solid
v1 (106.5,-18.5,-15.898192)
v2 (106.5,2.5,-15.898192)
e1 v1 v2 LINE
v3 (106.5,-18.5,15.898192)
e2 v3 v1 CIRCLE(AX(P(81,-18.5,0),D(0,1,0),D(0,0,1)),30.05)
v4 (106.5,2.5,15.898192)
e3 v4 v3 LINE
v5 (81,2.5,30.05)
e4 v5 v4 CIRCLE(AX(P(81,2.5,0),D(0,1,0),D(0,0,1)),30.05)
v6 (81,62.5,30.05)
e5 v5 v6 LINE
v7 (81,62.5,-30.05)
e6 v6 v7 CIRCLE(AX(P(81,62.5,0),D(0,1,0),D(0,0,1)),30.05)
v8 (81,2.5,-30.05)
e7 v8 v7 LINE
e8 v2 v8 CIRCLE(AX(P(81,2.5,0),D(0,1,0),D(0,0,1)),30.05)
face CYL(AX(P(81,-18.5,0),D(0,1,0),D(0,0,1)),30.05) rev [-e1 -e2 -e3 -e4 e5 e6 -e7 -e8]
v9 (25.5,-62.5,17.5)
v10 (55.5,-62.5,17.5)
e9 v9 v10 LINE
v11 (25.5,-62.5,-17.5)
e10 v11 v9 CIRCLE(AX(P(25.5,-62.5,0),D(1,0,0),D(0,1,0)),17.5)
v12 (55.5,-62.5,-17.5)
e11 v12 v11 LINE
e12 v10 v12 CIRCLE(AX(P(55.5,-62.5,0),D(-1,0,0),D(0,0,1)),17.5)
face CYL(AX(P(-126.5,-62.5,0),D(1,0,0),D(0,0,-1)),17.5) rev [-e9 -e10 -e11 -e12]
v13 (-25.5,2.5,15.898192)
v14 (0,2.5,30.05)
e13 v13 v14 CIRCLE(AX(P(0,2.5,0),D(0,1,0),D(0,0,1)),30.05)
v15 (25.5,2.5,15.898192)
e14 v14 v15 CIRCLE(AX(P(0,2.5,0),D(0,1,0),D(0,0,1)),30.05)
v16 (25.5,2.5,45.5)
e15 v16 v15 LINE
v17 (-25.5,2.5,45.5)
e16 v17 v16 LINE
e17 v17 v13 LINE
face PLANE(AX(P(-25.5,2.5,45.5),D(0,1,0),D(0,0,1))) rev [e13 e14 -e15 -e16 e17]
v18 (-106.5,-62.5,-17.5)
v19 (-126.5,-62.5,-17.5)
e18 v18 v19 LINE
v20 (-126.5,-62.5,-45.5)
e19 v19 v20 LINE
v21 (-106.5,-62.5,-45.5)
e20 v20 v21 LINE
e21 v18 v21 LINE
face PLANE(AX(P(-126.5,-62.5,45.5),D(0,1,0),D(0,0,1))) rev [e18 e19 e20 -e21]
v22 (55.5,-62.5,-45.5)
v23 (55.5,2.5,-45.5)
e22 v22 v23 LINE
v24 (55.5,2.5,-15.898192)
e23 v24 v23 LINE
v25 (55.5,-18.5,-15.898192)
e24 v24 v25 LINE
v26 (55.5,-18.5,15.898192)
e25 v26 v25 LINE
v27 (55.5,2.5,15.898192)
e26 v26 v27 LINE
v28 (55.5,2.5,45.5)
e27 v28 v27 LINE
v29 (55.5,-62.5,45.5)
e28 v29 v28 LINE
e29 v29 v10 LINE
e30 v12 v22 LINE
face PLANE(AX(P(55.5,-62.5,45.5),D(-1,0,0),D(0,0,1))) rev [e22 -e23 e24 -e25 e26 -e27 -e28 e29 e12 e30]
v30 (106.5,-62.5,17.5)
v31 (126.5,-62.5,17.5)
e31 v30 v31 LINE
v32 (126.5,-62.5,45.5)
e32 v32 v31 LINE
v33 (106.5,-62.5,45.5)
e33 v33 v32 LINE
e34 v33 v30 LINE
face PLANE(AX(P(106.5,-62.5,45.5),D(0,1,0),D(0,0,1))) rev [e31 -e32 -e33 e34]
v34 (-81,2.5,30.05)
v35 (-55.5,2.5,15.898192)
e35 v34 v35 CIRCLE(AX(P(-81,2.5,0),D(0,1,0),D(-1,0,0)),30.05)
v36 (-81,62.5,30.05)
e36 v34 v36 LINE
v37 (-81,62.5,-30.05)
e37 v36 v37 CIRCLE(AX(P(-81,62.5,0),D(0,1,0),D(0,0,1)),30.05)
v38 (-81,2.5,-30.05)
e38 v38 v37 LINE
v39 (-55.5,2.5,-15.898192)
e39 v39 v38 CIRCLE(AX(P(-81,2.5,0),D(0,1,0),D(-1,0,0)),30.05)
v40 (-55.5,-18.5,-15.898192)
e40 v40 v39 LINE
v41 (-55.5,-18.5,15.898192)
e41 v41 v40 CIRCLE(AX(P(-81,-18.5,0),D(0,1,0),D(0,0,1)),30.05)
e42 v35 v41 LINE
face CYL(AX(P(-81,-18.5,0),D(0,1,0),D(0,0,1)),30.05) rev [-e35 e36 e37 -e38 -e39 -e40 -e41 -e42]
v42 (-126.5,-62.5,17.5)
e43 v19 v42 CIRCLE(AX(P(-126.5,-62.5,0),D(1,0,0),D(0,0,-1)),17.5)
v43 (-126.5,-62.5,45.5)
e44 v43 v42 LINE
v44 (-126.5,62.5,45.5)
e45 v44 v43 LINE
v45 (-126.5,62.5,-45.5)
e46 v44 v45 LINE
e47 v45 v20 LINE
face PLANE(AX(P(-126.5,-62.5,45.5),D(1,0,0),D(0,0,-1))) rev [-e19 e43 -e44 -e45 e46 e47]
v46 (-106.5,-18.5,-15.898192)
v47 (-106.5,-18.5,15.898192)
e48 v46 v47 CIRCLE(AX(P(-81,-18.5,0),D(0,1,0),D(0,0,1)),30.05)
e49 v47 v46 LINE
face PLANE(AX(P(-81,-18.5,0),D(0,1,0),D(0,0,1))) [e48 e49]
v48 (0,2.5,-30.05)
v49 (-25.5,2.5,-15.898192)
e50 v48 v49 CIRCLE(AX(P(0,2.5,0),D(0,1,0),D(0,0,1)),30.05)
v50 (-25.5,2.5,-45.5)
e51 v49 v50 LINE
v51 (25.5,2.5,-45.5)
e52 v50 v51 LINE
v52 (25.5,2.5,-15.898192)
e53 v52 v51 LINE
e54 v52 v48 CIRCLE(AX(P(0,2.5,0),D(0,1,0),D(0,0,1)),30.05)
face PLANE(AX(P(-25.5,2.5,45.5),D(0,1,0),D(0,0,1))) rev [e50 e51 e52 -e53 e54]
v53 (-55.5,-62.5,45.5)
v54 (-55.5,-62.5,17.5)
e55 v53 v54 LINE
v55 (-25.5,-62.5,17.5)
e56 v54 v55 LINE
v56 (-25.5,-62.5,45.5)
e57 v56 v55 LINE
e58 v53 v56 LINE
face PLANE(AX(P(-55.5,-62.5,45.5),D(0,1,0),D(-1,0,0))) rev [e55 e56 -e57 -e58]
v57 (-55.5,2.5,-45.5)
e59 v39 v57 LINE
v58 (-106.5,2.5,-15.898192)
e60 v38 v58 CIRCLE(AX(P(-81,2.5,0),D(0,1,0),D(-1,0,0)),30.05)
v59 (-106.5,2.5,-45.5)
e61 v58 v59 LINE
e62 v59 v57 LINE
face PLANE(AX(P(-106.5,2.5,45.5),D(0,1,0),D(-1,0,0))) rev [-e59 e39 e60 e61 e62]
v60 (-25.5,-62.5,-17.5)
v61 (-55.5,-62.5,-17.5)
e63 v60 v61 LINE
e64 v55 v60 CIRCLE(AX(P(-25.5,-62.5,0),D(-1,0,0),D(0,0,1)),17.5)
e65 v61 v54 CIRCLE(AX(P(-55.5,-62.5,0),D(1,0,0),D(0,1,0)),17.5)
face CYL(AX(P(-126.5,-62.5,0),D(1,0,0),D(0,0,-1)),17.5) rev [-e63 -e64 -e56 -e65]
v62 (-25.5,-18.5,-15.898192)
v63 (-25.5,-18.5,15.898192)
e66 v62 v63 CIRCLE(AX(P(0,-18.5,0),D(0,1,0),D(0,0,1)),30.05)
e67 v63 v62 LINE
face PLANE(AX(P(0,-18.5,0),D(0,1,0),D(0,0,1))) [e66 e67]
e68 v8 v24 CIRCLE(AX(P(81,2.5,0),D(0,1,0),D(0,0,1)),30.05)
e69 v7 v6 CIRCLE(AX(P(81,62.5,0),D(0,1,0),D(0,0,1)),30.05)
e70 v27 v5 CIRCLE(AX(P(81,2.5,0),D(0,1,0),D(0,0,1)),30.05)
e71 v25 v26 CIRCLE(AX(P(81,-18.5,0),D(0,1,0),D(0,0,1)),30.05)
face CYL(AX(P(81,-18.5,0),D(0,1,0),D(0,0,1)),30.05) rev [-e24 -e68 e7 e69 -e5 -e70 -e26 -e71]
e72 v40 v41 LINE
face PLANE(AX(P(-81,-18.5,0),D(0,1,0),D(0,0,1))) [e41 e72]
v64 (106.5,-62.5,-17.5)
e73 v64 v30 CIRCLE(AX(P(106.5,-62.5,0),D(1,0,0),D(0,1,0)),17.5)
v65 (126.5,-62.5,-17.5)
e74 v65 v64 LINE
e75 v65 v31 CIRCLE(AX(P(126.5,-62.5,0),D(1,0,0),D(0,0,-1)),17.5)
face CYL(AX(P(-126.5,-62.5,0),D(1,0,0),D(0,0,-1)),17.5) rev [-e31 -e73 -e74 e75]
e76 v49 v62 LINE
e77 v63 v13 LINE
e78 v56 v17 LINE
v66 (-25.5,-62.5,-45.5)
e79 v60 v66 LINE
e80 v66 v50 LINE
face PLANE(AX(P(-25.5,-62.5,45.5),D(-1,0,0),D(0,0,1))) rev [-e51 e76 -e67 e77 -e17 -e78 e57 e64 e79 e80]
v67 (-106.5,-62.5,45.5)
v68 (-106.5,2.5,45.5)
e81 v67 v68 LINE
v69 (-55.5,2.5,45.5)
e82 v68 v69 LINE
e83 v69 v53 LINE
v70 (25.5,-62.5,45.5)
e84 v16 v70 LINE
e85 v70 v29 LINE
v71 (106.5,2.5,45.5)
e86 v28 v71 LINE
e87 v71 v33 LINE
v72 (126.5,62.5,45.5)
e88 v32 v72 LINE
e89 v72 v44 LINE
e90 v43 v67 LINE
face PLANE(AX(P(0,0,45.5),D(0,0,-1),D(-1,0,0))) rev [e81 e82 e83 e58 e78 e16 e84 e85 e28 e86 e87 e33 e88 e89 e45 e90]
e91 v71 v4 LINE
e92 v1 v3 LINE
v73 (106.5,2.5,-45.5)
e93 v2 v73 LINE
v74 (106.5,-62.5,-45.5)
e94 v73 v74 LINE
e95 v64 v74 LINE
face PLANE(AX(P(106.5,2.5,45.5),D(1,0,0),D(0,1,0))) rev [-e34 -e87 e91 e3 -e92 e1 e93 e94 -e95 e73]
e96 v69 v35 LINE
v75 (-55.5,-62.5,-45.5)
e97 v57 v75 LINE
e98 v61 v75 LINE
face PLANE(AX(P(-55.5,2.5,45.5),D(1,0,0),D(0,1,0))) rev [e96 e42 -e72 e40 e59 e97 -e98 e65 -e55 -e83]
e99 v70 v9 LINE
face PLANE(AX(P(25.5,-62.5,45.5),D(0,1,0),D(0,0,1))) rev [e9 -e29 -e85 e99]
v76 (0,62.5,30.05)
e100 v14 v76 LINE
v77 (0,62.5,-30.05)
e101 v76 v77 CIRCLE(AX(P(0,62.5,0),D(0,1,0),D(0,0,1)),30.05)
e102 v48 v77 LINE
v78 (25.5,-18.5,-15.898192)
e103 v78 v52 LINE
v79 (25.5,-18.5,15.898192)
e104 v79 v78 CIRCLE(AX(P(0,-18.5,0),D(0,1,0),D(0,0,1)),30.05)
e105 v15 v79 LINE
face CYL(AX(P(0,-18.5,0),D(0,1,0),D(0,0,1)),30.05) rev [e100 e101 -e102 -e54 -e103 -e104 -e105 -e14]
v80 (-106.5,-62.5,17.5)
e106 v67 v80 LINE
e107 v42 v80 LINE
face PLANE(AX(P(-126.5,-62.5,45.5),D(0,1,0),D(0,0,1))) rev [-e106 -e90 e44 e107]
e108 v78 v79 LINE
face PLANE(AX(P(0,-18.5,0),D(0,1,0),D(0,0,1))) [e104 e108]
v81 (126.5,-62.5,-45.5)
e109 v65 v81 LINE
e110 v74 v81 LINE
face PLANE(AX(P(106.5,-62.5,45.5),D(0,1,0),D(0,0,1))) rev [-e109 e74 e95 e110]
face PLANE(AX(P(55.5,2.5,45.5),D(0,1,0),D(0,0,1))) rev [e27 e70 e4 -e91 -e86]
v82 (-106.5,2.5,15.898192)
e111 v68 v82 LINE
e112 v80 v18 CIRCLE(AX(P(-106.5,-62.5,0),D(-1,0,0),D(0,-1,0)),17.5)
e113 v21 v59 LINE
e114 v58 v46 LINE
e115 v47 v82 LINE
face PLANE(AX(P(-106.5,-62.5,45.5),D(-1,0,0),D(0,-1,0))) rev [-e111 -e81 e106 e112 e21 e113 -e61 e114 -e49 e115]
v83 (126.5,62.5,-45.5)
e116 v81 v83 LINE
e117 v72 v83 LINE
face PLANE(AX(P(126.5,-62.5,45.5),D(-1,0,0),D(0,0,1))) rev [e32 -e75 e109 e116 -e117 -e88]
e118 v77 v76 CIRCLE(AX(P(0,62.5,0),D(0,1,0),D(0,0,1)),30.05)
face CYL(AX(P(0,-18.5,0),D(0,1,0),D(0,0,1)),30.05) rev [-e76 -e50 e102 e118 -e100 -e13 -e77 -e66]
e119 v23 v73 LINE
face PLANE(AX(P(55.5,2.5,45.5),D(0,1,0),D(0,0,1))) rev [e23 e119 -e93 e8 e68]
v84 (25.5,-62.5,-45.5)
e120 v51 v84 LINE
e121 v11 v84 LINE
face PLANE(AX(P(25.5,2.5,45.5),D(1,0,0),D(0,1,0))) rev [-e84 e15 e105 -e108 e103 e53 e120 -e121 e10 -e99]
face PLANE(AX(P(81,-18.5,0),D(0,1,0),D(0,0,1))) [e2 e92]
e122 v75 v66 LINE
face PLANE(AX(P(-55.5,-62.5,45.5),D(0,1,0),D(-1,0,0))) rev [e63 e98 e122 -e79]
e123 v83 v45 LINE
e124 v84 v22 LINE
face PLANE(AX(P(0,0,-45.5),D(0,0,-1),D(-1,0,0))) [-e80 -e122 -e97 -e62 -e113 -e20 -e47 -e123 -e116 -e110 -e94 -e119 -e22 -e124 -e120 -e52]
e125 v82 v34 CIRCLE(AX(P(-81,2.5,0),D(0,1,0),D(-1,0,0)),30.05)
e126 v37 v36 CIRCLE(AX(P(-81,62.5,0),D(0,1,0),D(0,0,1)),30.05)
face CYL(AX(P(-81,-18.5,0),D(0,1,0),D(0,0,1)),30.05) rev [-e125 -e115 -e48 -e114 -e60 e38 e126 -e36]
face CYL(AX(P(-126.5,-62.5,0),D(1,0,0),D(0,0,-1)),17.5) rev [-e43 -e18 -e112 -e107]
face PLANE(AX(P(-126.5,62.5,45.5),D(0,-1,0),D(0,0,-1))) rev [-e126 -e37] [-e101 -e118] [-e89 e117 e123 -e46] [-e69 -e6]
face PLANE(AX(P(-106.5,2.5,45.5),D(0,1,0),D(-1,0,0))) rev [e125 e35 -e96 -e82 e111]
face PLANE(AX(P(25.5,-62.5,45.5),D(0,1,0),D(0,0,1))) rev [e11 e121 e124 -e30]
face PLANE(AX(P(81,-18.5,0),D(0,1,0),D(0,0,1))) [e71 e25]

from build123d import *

# Parameters (mm, degrees)
BLOCK_BODY_DEPTH             = 45.5
CRANKSHAFT_BORE_SKETCH_R     = 17.5
CRANKSHAFT_BORE_35_DEPTH     = 265.547727263
CYLINDER_BORES_SKETCH_R      = 30.05
CYLINDER_BORES_3X_45_5_DEPTH = 81


with BuildPart() as part:
    # Block Profile Sketch → Block Body (new, symmetric)
    with BuildSketch(Plane.XY):
        Polygon((-106.5, -62.5), (-106.5, 2.5), (-55.5, 2.5), (-55.5, -62.5), (-25.5, -62.5), (-25.5, 2.5), (25.5, 2.5), (25.5, -62.5), (55.5, -62.5), (55.5, 2.5), (106.5, 2.5), (106.5, -62.5), (126.5, -62.5), (126.5, 62.5), (-126.5, 62.5), (-126.5, -62.5), align=None)
    extrude(amount=BLOCK_BODY_DEPTH, both=True)

    # Crankshaft Bore Sketch → Crankshaft Bore Ø35 (cut, through all)
    with BuildSketch(Plane(origin=(126.5, 0, 0), x_dir=(0, 0, -1), z_dir=(1, 0, 0))):
        with Locations((0, -62.5)):
            Circle(CRANKSHAFT_BORE_SKETCH_R)
    extrude(amount=-CRANKSHAFT_BORE_35_DEPTH, mode=Mode.SUBTRACT)

    # Cylinder Bores Sketch → Cylinder Bores 3xØ45.5 (cut)
    with BuildSketch(Plane(origin=(0, 62.5, 0), x_dir=(1, 0, 0), z_dir=(0, 1, 0))):
        with Locations(Location((-81, 0, 0), (0, 0, 270))):
            Circle(CYLINDER_BORES_SKETCH_R)
        with Locations(Location((0, 0, 0), (0, 0, 270))):
            Circle(CYLINDER_BORES_SKETCH_R)
        with Locations(Location((81, 0, 0), (0, 0, 270))):
            Circle(CYLINDER_BORES_SKETCH_R)
    extrude(amount=-CYLINDER_BORES_3X_45_5_DEPTH, mode=Mode.SUBTRACT)


solid = part.part
